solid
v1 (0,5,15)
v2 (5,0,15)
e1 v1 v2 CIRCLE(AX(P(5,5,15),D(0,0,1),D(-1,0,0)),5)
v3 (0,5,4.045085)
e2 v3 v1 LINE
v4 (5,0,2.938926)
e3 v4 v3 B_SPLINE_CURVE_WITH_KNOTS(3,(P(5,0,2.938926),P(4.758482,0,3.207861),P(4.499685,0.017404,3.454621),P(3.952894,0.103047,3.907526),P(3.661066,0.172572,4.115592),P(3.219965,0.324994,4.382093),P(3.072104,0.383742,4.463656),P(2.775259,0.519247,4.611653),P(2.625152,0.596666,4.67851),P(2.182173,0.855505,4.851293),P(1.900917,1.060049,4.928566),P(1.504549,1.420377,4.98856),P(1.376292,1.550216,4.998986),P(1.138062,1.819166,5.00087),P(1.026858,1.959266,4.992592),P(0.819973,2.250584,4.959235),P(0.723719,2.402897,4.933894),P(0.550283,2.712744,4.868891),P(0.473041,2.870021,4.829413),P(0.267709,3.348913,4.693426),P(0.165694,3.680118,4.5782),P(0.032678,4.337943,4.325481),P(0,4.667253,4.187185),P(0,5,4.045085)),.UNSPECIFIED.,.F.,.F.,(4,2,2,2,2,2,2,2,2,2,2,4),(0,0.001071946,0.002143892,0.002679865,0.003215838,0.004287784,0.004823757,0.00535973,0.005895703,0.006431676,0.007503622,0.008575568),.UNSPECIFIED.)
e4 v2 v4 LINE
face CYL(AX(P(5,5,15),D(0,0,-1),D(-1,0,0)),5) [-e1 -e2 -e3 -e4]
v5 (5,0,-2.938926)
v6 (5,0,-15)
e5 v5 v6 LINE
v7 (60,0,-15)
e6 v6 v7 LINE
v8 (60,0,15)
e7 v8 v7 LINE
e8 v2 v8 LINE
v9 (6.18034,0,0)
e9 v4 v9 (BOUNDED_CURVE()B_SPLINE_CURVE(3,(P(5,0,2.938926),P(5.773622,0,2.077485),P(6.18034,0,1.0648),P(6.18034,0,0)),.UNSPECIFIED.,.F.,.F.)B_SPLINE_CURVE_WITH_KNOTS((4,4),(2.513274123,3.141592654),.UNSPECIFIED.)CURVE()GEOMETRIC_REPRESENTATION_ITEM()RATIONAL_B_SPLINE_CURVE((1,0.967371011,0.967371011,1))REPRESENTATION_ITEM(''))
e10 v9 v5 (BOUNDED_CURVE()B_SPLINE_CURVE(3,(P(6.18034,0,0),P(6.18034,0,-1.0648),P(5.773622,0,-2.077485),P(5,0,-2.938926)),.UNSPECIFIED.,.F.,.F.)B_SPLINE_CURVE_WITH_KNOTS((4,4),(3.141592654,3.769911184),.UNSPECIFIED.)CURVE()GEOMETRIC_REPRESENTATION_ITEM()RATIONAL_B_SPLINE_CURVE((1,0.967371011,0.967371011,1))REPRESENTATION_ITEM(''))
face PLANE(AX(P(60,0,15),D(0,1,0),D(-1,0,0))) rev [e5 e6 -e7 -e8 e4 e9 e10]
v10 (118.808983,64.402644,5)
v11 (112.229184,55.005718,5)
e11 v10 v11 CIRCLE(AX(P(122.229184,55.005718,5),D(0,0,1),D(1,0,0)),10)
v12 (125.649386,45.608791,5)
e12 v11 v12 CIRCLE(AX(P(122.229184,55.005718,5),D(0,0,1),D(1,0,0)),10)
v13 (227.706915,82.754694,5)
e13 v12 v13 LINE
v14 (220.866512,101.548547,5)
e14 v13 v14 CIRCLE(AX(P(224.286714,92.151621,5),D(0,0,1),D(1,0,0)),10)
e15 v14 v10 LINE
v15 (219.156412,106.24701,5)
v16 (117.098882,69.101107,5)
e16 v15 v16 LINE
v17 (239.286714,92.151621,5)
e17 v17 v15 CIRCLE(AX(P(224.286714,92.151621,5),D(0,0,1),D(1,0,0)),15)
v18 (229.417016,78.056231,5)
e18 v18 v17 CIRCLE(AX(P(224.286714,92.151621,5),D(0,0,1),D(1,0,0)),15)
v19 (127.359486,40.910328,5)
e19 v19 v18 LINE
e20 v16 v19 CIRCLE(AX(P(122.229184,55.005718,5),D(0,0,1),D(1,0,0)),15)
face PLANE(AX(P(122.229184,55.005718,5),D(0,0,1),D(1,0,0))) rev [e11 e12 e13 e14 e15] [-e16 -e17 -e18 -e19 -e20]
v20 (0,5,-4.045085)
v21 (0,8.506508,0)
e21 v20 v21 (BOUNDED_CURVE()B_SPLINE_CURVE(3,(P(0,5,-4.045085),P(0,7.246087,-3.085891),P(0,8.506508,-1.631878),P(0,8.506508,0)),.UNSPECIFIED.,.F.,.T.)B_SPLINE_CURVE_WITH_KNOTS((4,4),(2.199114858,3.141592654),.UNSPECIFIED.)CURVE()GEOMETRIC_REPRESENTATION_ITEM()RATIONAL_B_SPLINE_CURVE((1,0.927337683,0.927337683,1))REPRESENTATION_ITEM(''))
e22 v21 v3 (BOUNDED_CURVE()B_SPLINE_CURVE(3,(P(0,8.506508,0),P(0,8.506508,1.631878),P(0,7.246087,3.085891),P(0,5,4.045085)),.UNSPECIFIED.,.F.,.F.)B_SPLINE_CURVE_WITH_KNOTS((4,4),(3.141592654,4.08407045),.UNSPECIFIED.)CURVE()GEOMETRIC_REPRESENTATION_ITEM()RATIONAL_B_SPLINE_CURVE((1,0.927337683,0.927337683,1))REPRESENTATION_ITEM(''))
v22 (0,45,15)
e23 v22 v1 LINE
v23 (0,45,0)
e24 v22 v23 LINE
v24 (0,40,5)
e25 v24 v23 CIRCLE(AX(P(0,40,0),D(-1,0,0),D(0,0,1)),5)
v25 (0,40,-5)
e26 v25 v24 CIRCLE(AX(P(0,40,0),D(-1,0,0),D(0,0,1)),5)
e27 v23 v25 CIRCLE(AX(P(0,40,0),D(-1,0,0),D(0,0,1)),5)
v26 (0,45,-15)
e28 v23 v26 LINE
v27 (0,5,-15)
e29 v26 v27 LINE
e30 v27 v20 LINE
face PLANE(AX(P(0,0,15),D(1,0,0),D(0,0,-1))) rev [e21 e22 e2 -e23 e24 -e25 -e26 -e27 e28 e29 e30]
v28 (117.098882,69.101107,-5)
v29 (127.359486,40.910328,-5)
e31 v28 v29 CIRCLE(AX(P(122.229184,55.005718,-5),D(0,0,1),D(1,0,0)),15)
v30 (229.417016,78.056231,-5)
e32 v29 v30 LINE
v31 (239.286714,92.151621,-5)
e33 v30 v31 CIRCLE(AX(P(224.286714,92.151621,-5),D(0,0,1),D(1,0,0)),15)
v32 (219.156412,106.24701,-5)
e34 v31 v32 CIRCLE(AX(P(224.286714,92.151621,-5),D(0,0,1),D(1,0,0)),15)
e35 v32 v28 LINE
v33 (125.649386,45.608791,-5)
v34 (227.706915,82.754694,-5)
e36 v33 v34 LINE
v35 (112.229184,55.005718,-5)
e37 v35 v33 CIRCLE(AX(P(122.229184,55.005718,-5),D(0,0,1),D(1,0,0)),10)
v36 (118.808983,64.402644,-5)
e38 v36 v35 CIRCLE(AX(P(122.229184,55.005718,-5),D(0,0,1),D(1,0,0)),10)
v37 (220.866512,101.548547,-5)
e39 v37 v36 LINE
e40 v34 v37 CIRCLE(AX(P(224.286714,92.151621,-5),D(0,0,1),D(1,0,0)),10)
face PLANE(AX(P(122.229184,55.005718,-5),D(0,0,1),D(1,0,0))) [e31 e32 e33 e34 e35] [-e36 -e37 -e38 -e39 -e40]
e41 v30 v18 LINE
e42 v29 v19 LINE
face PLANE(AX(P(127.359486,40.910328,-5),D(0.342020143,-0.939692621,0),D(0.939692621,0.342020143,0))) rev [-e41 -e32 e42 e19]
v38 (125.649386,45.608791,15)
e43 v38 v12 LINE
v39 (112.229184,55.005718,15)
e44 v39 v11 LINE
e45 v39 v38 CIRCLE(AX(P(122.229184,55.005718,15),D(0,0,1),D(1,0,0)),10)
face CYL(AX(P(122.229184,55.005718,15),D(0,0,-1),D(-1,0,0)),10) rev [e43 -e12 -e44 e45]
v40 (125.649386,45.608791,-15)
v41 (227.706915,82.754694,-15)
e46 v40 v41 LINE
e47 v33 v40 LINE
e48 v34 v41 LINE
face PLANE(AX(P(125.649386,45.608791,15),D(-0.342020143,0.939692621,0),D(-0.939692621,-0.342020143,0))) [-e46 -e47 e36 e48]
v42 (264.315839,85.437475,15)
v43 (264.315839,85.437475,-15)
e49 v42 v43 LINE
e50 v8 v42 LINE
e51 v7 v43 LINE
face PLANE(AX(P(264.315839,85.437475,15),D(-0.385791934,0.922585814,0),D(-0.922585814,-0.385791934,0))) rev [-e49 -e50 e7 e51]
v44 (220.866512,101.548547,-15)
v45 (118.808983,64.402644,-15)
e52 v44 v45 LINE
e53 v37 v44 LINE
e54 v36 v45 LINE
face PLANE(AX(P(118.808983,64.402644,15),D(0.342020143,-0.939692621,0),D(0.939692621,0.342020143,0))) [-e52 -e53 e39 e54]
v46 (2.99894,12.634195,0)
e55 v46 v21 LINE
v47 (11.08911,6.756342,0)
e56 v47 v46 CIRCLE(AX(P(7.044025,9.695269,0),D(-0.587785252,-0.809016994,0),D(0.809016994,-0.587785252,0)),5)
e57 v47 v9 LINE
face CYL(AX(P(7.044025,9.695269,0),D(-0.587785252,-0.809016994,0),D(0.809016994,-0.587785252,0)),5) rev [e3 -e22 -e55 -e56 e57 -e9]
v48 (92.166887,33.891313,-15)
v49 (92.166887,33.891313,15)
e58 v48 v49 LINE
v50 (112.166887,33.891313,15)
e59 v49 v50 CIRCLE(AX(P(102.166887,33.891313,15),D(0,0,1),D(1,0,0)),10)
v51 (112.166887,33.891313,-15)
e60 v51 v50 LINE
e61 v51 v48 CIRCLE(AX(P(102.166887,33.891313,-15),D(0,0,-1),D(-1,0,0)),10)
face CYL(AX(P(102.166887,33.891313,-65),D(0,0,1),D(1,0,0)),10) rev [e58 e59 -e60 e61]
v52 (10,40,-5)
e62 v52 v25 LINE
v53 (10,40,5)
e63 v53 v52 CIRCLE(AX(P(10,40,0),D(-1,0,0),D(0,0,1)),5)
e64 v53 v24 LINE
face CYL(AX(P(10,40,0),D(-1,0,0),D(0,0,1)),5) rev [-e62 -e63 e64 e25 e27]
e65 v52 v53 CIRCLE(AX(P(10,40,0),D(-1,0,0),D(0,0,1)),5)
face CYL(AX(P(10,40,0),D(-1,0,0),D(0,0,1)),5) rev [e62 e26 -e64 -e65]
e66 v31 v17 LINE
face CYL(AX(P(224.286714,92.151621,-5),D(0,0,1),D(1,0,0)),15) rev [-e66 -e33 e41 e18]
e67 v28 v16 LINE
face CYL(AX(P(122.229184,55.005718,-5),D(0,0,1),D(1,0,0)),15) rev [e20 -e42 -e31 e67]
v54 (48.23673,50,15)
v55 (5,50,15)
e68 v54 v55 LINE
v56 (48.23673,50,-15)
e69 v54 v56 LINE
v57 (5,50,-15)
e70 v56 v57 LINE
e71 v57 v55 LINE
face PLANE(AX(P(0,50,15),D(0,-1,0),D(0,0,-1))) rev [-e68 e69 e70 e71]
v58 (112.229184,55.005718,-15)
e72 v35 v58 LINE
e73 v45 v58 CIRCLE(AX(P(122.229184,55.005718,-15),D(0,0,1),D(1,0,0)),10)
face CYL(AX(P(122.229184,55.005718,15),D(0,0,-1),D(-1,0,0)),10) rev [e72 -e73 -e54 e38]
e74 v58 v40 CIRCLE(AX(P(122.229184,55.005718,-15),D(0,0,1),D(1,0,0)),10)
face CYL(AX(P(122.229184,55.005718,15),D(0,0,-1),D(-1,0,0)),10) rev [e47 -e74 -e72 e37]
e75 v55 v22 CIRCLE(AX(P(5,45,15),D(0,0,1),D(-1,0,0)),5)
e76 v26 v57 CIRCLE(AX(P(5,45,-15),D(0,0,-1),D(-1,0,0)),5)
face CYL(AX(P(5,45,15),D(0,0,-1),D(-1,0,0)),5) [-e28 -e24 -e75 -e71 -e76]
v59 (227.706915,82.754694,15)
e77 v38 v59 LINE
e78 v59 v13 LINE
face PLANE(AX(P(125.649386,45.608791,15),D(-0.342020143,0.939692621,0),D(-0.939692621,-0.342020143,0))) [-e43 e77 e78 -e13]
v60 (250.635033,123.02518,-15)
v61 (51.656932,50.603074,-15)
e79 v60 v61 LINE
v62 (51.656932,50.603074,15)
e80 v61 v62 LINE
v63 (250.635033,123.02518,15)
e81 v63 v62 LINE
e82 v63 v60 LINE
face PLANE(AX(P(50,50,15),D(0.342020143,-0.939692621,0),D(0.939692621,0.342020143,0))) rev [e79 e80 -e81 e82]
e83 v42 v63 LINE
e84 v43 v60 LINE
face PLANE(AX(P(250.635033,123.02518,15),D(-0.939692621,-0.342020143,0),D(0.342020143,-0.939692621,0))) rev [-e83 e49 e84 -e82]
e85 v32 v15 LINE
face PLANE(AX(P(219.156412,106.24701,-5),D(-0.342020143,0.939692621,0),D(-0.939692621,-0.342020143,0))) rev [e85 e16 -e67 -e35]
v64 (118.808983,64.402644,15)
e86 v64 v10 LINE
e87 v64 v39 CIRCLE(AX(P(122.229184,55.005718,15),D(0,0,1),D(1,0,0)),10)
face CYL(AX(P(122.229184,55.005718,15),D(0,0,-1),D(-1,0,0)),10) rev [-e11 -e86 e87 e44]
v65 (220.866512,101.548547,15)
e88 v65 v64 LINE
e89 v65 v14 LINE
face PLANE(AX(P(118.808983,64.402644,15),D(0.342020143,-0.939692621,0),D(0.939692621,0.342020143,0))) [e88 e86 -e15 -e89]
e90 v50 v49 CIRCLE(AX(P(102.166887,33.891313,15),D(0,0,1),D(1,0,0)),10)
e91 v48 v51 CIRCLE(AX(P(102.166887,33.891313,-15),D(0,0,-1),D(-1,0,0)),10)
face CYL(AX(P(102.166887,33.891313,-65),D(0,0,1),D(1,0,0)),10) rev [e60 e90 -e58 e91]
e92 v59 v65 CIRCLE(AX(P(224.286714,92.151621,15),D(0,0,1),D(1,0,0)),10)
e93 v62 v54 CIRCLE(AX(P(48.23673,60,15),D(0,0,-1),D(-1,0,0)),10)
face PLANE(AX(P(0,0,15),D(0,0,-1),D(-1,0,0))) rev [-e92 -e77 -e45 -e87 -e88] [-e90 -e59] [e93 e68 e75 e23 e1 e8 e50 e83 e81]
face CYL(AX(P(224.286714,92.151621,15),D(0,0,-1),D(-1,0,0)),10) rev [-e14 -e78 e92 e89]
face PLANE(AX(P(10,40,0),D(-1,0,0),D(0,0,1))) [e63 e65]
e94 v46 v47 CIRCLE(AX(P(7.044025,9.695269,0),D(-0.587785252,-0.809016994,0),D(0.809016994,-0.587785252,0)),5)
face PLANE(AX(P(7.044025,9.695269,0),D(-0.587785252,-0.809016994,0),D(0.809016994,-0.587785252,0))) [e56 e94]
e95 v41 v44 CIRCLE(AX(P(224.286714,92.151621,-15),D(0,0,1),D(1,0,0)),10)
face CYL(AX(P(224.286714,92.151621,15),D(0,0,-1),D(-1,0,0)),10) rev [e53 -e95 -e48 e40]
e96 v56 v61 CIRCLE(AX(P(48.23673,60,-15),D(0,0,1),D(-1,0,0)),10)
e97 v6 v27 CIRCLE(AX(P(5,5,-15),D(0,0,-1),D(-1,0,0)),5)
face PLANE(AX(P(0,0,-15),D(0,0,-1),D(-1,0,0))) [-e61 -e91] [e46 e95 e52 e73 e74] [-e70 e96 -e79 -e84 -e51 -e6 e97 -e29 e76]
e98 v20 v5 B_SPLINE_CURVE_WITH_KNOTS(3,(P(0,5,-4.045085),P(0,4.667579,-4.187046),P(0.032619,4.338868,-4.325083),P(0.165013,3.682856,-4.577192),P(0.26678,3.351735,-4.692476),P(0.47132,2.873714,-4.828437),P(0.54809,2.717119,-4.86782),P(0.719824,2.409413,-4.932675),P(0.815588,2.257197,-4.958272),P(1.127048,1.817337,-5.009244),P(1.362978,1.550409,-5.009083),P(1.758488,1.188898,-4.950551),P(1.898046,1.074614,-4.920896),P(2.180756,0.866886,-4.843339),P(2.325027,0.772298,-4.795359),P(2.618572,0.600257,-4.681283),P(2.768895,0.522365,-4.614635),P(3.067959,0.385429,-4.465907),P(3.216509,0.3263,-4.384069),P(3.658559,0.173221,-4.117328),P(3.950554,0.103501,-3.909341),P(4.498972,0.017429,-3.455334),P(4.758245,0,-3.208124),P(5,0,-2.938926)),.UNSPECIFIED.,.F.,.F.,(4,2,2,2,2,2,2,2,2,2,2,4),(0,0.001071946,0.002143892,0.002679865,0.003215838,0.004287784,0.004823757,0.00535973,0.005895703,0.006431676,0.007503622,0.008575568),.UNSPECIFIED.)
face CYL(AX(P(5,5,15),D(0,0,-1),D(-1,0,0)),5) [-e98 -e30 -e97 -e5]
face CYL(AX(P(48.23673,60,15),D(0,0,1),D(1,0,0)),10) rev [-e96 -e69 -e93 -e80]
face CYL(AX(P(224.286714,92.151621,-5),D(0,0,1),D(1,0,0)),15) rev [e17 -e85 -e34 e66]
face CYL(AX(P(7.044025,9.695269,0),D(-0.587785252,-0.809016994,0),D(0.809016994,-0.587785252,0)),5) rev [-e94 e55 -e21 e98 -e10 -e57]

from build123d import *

# Parameters (mm, degrees)
BOSS_EXTRUDE1_DEPTH = 15
FILLET1_R           = 10
FILLET2_R           = 5
SKETCH2_R           = 5
CUT_EXTRUDE1_DEPTH  = 10
SKETCH3_R           = 5
CUT_EXTRUDE2_DEPTH  = 10
SKETCH5_R           = 10
BOSS_EXTRUDE3_DEPTH = 10
SKETCH6_R           = 7.5
BOSS_EXTRUDE4_DEPTH = 5
SKETCH7_R           = 10
BOSS_EXTRUDE5_DEPTH = 2
SKETCH8_R           = 10
CUT_EXTRUDE3_DEPTH  = 80
CUT_EXTRUDE4_DEPTH  = 5
SKETCH10_W          = 33.070840011
SKETCH10_H          = 51.47652372
CUT_EXTRUDE5_DEPTH  = 50


with BuildPart() as part:
    # Sketch1 → Boss-Extrude1 (new, symmetric)
    with BuildSketch(Plane.XY):
        Polygon((0, 0), (0, 50), (50, 50), (250.63503339, 123.025180105), (264.315839123, 85.437475274), (60, 0), align=None)
        with BuildLine():
            Line((118.808982902, 64.402643902), (220.866512245, 101.548546765))
            ThreePointArc((220.866512245, 101.548546765), (233.683639886, 95.571821991), (227.706915111, 82.75469435))
            Line((227.706915111, 82.75469435), (125.649385769, 45.608791486))
            ThreePointArc((125.649385769, 45.608791486), (112.832258128, 51.585516261), (118.808982902, 64.402643902))
        make_face(mode=Mode.SUBTRACT)
    extrude(amount=BOSS_EXTRUDE1_DEPTH, both=True)

    # Fillet1
    fillet1_edges = [part.edges().sort_by_distance(p)[0] for p in [
        (50, 50, 0),
    ]]
    fillet(fillet1_edges, radius=FILLET1_R)

    # Fillet2
    fillet2_edges = [part.edges().sort_by_distance(p)[0] for p in [
        (0, 0, 0),
        (0, 50, 0),
    ]]
    fillet(fillet2_edges, radius=FILLET2_R)

    # Sketch2 → Cut-Extrude1 (cut)
    with BuildSketch(Plane(origin=(1.166172543, 1.605098805, 0), x_dir=(0, 0, -1), z_dir=(-0.587785252292477, -0.8090169943749446, 0))):
        with Locations(Location((0, 0, 0), (0, 0, 90))):
            Circle(SKETCH2_R)
    extrude(amount=-CUT_EXTRUDE1_DEPTH, mode=Mode.SUBTRACT)

    # Sketch3 → Cut-Extrude2 (cut)
    with BuildSketch(Plane.ZY):
        with Locations((0, 40)):
            Circle(SKETCH3_R)
    extrude(amount=-CUT_EXTRUDE2_DEPTH, mode=Mode.SUBTRACT)

    # Sketch5 → Boss-Extrude3 (add)
    with BuildSketch(Plane(origin=(0, 0, -15), x_dir=(-1, 0, 0), z_dir=(0, 0, -1))):
        with Locations((-15, 25.111581997)):
            Circle(SKETCH5_R)
    extrude(amount=BOSS_EXTRUDE3_DEPTH)

    # Sketch6 → Boss-Extrude4 (add)
    with BuildSketch(Plane(origin=(0, 0, -25), x_dir=(-1, 0, 0), z_dir=(0, 0, -1))):
        with Locations((-15, 25.111581997)):
            Circle(SKETCH6_R)
    extrude(amount=BOSS_EXTRUDE4_DEPTH)

    # Sketch7 → Boss-Extrude5 (add)
    with BuildSketch(Plane(origin=(0, 0, -30), x_dir=(-1, 0, 0), z_dir=(0, 0, -1))):
        with Locations((-15, 25.111581997)):
            Circle(SKETCH7_R)
    extrude(amount=BOSS_EXTRUDE5_DEPTH)

    # Sketch8 → Cut-Extrude3 (cut)
    with BuildSketch(Plane.XY.offset(15)):
        with Locations((102.166886521, 33.891313111)):
            Circle(SKETCH8_R)
    extrude(amount=-CUT_EXTRUDE3_DEPTH, mode=Mode.SUBTRACT)

    # Sketch9 → Cut-Extrude4 (cut, symmetric)
    with BuildSketch(Plane.XY):
        with BuildLine():
            Line((127.359486485, 40.910328382), (229.417015828, 78.056231246))
            ThreePointArc((229.417015828, 78.056231246), (238.38210299, 97.281922707), (219.156411528, 106.247009869))
            Line((219.156411528, 106.247009869), (117.098882186, 69.101107006))
            ThreePointArc((117.098882186, 69.101107006), (108.133795024, 49.875415544), (127.359486485, 40.910328382))
        make_face()
        with BuildLine():
            Line((220.866512245, 101.548546765), (118.808982902, 64.402643902))
            ThreePointArc((118.808982902, 64.402643902), (112.832258128, 51.585516261), (125.649385769, 45.608791486))
            Line((125.649385769, 45.608791486), (227.706915111, 82.75469435))
            ThreePointArc((227.706915111, 82.75469435), (233.683639886, 95.571821991), (220.866512245, 101.548546765))
        make_face(mode=Mode.SUBTRACT)
    extrude(amount=CUT_EXTRUDE4_DEPTH, both=True, mode=Mode.SUBTRACT)

    # Sketch10 → Cut-Extrude5 (cut)
    with BuildSketch(Plane.ZY):
        with Locations((-31.535420006, 25.73826186)):
            Rectangle(SKETCH10_W, SKETCH10_H)
    extrude(amount=-CUT_EXTRUDE5_DEPTH, mode=Mode.SUBTRACT)


solid = part.part
